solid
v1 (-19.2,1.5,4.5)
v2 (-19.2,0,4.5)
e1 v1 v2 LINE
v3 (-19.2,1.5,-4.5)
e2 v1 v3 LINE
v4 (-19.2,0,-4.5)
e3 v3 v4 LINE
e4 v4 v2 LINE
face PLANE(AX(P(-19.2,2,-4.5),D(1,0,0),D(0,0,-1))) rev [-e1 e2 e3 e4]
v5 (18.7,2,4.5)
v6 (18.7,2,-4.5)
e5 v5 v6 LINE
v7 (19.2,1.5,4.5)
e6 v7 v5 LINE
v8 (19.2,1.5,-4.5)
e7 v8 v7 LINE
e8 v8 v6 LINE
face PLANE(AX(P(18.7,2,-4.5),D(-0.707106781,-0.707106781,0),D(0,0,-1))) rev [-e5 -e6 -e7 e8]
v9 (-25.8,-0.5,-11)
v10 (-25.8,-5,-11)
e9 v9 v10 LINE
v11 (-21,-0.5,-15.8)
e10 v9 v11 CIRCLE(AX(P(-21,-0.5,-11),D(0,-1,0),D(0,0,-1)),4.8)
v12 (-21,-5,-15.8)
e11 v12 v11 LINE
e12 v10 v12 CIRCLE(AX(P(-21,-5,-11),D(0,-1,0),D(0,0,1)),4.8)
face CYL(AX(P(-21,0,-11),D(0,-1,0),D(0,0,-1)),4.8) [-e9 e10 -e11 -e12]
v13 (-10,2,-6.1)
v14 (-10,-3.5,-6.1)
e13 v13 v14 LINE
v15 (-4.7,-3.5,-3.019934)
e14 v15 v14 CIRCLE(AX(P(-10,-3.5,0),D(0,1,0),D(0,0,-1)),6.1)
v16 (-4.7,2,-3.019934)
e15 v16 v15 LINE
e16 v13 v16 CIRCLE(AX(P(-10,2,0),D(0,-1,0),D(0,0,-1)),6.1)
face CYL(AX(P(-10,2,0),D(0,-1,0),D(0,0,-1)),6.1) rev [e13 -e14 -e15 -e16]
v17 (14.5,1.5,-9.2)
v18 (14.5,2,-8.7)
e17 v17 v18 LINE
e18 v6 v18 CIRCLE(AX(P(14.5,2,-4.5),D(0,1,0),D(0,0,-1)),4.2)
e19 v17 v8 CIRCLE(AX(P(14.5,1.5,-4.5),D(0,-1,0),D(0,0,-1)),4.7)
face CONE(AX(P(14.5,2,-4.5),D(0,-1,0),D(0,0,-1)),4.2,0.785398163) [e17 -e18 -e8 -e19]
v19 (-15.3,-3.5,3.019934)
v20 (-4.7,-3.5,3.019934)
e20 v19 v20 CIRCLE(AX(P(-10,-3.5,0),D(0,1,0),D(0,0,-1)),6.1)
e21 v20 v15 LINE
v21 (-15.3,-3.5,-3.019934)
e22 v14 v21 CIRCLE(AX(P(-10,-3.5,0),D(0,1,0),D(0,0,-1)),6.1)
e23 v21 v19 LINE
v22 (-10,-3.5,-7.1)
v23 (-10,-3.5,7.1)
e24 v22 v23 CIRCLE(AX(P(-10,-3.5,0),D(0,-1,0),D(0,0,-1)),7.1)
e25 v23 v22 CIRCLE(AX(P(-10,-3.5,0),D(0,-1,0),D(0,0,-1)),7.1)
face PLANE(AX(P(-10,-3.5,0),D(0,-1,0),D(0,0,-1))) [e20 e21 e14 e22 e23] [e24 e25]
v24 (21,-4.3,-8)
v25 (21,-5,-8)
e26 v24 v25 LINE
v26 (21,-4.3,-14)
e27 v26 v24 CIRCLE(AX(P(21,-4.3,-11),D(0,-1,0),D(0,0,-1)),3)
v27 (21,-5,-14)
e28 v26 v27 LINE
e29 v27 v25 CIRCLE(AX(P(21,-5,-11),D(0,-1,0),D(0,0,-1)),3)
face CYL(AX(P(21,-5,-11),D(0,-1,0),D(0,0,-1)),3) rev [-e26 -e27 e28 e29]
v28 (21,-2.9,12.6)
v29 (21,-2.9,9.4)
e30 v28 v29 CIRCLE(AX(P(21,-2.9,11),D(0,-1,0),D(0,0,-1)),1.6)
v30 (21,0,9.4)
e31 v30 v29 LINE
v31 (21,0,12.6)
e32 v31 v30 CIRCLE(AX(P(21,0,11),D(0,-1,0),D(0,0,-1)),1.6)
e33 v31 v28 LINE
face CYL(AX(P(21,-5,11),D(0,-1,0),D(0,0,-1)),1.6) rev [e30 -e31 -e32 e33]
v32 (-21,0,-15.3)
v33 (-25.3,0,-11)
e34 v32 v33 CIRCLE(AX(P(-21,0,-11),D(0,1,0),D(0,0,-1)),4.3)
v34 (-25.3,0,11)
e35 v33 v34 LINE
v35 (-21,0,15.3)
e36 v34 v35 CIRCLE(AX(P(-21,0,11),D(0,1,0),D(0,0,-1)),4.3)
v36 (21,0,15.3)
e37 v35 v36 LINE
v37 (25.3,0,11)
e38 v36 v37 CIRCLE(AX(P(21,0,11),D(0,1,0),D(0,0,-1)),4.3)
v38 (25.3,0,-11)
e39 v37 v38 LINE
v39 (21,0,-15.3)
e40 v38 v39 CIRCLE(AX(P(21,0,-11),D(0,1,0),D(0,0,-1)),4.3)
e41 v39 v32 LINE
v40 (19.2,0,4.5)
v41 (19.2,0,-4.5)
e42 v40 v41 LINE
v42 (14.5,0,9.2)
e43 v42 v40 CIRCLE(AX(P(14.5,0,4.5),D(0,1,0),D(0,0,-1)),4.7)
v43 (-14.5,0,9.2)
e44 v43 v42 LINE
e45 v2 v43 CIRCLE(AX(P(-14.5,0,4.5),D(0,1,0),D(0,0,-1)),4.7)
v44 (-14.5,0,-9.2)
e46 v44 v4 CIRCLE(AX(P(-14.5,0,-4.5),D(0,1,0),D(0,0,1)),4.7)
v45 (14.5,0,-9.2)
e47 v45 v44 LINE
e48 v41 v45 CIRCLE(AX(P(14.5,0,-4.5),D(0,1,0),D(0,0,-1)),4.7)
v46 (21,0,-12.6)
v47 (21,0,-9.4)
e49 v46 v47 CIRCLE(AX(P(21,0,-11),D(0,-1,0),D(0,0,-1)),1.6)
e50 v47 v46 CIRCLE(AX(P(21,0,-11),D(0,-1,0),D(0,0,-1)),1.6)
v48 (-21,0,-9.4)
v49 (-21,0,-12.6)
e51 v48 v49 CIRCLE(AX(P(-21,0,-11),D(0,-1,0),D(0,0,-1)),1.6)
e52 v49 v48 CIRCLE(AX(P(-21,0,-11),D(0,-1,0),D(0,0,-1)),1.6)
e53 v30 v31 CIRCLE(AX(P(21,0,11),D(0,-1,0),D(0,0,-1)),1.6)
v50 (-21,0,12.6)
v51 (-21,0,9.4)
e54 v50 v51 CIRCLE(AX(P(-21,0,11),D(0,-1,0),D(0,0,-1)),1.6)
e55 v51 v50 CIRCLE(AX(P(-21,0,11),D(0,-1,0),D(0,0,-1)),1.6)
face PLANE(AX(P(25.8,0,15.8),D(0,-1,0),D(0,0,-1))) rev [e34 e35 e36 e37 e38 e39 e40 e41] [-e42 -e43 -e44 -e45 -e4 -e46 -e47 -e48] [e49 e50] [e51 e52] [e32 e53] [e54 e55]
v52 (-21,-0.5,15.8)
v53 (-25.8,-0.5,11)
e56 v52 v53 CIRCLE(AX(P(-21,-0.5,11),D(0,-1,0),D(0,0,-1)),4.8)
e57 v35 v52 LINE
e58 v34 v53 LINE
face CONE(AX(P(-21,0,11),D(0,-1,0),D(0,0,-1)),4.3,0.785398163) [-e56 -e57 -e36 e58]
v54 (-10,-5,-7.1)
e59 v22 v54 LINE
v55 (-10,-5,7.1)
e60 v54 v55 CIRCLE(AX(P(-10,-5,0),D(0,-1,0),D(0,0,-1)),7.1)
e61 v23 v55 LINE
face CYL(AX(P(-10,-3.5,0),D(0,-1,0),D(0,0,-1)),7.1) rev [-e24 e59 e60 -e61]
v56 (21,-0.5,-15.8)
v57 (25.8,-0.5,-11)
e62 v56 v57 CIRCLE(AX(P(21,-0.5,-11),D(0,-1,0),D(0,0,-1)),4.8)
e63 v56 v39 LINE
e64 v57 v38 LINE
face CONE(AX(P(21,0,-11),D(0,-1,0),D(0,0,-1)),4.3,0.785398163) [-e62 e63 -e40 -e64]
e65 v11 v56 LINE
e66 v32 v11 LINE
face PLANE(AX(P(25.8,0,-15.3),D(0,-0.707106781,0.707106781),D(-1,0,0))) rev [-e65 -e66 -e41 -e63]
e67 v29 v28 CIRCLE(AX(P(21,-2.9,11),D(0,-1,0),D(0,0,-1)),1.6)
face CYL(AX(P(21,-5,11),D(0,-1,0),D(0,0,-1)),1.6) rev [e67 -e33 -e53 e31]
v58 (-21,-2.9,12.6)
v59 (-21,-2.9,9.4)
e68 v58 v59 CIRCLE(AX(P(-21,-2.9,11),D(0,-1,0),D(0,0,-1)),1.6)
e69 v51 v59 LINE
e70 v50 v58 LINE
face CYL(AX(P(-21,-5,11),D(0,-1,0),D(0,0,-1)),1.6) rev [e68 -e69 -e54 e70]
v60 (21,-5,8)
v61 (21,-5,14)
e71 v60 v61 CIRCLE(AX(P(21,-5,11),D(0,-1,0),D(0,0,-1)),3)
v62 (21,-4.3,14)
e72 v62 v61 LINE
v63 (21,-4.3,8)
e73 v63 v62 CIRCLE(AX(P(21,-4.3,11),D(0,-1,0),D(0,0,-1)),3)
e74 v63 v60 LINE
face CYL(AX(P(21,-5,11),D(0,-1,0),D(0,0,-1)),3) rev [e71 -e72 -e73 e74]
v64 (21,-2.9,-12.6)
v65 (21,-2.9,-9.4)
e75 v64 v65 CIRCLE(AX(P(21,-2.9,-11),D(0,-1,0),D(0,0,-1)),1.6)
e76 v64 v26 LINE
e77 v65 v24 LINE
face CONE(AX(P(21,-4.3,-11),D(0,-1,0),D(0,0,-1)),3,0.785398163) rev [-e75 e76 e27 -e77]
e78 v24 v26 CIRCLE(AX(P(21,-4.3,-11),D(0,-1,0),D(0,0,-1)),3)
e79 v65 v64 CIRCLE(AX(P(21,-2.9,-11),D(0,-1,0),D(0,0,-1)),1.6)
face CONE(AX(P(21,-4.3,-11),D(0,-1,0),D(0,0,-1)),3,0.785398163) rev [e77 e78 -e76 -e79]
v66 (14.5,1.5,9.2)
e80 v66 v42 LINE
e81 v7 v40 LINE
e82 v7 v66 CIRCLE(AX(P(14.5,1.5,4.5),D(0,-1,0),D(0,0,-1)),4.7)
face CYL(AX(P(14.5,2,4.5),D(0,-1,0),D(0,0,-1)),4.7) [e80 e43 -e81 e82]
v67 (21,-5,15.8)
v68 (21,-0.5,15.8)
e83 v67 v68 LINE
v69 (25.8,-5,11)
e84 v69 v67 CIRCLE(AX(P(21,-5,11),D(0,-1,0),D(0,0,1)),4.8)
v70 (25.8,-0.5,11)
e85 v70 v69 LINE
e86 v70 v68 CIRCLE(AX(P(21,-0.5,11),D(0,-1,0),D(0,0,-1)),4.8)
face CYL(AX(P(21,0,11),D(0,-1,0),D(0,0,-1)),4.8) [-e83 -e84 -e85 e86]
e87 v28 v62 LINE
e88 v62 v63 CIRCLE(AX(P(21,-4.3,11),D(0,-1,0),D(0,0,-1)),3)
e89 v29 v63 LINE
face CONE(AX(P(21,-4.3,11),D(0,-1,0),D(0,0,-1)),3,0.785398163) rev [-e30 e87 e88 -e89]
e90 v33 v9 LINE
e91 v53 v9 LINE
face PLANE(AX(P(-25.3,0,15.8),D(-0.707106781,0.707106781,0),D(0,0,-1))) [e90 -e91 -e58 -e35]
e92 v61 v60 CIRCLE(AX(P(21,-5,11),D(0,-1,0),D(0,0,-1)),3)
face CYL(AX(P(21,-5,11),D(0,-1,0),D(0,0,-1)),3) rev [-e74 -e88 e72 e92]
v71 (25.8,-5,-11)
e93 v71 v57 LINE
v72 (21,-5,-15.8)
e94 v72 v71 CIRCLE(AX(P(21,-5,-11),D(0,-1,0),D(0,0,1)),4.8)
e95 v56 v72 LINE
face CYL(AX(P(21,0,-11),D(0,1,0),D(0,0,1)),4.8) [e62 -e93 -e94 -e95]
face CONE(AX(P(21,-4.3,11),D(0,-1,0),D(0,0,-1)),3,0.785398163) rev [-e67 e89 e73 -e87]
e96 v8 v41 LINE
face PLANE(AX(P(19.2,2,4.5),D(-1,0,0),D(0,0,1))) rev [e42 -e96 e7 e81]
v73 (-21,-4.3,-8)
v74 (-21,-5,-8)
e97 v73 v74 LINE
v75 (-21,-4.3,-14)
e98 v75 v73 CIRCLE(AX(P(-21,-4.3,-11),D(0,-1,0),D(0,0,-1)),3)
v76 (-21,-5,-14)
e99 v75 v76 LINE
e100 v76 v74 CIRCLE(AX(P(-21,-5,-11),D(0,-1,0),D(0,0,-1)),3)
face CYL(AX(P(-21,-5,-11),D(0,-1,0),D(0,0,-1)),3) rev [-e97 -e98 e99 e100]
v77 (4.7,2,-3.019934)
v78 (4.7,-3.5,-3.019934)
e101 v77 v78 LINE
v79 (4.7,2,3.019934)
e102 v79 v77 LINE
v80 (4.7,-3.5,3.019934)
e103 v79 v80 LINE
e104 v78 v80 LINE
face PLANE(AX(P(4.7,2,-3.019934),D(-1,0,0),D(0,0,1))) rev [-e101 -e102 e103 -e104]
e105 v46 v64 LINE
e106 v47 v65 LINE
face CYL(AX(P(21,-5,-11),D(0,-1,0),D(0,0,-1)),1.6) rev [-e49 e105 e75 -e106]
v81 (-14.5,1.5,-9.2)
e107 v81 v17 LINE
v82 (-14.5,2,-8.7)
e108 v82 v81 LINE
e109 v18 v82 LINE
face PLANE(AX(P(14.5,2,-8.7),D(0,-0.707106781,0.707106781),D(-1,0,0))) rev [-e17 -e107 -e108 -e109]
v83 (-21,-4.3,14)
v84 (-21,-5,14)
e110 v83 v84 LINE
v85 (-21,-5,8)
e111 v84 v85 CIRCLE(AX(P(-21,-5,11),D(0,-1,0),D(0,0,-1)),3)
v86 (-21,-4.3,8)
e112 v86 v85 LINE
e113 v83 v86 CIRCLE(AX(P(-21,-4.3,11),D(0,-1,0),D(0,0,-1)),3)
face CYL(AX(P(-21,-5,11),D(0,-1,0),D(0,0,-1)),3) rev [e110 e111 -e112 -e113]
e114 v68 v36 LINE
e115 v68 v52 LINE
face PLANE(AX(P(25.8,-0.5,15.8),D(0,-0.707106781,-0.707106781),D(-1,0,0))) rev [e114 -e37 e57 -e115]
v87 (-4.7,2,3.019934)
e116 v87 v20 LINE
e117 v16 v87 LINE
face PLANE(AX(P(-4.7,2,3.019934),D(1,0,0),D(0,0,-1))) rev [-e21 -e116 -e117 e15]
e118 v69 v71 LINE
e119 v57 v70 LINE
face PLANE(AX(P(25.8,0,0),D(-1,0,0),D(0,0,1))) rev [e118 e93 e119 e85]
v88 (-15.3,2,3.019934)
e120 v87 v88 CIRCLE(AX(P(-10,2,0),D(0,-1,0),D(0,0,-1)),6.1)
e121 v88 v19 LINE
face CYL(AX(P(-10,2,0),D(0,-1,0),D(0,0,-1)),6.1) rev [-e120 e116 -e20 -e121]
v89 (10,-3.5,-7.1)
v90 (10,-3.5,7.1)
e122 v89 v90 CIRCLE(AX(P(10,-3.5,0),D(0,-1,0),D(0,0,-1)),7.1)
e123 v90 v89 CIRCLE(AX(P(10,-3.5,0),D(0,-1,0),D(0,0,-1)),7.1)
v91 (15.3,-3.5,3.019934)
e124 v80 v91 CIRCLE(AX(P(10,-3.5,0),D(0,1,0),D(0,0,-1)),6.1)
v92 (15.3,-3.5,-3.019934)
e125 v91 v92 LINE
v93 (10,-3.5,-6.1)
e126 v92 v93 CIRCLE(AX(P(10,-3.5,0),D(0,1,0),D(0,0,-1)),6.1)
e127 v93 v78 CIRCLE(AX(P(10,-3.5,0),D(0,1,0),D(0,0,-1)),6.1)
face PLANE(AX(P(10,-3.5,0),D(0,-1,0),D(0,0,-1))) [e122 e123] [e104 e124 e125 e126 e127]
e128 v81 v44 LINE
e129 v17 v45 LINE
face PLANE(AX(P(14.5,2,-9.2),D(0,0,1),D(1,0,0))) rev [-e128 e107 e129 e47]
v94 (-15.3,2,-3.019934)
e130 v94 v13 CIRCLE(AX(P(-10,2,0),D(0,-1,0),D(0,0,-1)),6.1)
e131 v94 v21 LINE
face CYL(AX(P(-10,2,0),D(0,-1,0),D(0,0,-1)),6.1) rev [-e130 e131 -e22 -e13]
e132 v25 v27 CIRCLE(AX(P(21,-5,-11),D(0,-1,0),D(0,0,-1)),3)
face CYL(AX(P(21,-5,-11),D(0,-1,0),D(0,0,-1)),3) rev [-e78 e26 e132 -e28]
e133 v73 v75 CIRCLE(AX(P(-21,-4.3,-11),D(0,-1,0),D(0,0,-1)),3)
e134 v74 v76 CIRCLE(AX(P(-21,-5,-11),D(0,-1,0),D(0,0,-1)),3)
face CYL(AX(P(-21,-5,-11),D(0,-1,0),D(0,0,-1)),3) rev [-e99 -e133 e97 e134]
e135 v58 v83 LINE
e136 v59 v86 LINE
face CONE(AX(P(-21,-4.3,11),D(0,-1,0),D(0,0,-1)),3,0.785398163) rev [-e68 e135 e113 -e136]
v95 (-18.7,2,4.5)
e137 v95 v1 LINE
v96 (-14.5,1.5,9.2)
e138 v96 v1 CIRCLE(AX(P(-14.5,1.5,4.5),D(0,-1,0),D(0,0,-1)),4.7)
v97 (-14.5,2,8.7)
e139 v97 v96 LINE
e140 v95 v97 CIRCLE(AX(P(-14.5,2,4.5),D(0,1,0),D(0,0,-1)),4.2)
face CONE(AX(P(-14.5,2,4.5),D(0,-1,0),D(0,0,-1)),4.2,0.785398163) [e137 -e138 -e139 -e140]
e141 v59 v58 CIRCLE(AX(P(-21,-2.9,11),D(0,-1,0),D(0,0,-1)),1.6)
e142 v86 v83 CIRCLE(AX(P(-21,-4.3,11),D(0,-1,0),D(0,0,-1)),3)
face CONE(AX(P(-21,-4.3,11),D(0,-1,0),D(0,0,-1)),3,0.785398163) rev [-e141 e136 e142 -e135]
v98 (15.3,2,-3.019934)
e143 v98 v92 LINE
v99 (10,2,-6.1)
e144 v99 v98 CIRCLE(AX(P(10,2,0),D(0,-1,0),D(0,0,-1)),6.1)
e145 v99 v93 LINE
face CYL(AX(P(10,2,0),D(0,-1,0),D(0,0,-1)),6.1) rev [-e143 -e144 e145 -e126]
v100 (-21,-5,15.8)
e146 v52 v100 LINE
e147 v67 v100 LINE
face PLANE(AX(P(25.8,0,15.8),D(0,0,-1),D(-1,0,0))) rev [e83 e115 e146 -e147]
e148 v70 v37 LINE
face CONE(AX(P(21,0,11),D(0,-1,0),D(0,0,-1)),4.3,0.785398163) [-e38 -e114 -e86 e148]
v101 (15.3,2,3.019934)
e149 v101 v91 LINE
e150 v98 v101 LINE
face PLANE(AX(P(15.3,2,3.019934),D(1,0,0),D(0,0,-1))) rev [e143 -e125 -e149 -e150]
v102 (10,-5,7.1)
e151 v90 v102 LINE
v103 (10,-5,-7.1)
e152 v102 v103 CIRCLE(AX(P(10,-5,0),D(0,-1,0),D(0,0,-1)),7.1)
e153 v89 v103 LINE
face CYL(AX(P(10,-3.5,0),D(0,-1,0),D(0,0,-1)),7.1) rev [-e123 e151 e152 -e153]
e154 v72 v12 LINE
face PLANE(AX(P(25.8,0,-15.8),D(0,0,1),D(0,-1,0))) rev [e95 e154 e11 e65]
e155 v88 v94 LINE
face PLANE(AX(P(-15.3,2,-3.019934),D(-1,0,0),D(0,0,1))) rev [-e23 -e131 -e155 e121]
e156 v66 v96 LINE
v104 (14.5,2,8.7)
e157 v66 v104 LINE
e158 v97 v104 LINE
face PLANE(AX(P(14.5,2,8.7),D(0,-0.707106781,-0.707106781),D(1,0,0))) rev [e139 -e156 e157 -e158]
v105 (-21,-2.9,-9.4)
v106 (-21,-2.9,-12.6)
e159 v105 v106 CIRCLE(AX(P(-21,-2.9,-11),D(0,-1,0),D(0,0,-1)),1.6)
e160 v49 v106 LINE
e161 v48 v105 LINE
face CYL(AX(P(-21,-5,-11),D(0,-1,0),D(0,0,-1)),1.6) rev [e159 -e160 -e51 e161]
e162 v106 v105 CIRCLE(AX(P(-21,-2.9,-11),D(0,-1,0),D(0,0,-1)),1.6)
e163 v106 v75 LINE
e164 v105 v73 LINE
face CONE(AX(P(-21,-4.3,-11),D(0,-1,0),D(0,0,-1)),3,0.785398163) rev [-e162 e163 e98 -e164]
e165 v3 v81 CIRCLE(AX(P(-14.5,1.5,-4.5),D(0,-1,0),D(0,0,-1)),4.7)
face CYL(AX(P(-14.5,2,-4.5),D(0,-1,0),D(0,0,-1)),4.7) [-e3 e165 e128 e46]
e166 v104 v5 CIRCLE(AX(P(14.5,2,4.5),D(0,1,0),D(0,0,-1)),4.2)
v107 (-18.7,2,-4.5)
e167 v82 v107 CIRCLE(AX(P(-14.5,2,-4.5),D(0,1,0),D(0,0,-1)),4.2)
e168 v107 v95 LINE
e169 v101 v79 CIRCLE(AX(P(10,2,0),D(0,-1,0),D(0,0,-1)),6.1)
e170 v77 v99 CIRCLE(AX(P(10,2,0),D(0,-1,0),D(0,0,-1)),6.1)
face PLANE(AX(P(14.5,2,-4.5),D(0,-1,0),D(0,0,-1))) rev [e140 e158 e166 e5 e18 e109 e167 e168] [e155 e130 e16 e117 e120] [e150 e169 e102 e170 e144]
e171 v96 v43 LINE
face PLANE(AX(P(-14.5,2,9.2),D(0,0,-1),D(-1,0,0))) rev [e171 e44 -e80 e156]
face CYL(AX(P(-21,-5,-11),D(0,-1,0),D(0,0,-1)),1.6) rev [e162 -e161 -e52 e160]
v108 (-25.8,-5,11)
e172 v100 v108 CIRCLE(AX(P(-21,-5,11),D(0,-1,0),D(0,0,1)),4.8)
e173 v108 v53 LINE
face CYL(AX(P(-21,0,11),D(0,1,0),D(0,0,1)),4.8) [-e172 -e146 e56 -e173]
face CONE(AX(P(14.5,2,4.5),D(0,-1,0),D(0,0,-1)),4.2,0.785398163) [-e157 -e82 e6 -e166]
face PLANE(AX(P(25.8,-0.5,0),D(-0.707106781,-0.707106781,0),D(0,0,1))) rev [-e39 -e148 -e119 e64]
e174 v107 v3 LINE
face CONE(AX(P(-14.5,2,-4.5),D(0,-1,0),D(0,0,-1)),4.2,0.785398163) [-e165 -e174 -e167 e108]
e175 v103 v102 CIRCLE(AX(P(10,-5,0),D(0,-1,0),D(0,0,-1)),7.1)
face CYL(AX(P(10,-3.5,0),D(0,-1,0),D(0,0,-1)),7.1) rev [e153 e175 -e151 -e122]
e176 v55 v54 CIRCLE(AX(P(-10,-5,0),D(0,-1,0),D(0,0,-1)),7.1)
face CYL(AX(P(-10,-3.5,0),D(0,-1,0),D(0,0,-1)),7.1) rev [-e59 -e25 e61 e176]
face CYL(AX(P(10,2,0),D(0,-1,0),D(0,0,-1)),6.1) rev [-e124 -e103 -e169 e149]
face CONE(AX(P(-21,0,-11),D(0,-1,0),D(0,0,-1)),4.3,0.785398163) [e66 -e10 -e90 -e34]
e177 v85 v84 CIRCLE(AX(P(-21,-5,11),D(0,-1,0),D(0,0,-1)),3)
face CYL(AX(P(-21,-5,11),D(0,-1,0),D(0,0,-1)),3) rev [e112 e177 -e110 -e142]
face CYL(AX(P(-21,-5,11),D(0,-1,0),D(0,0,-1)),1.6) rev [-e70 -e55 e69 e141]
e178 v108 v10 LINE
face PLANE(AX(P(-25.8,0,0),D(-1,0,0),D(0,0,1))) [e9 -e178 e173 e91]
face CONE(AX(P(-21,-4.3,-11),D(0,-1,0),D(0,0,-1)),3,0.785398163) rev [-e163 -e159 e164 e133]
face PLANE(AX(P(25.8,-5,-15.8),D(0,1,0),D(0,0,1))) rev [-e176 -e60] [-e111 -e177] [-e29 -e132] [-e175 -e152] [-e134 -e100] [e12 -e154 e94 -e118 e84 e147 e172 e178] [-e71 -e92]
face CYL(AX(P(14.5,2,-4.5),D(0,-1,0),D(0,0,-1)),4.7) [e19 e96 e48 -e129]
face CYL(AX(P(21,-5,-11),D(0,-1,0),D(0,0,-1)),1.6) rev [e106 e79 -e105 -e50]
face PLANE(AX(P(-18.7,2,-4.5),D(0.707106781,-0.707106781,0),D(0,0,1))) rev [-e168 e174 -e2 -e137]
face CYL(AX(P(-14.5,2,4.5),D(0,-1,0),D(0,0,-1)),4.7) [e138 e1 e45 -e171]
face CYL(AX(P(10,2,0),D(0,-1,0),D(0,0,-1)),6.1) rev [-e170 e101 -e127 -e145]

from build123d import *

# Parameters (mm, degrees)
SKETCH_1_W               = 31.6
SKETCH_1_H               = 5
EXTRUDE_1_DEPTH          = 25.8
EXTRUDE_2_DEPTH          = 2
FILLET_1_R               = 4.8
CUT_EXTRUDE_1_DEPTH      = 32.052858162
SKETCH_4_R               = 7.1
CUT_EXTRUDE_2_DEPTH      = 1.5
CHAMFER_2_SIZE           = 0.5
HOLE_WIZARD_1_AT_2_COUNT = 2
HOLE_WIZARD_1_AT_2_PITCH = 42
HOLE_WIZARD_1_AT_3_COUNT = 2
HOLE_WIZARD_1_AT_3_PITCH = 47.413078365
HOLE_WIZARD_1_AT_4_COUNT = 2
HOLE_WIZARD_1_AT_4_PITCH = 22


with BuildPart() as part:
    # 草图1 → 凸台-拉伸1 (new, symmetric)
    with BuildSketch(Plane(origin=(0, 0, 0), x_dir=(0, 0, -1), z_dir=(1, 0, 0))):
        with Locations((0, -2.5)):
            Rectangle(SKETCH_1_W, SKETCH_1_H)
    extrude(amount=EXTRUDE_1_DEPTH, both=True)

    # 草图2 → 凸台-拉伸2 (add)
    with BuildSketch(Plane(origin=(0, 0, 0), x_dir=(1, 0, 0), z_dir=(0, 1, 0))):
        with BuildLine():
            Line((-19.2, 4.5), (-19.2, -4.5))
            ThreePointArc((-19.2, -4.5), (-17.823401872, -7.823401872), (-14.5, -9.2))
            Line((-14.5, -9.2), (14.5, -9.2))
            ThreePointArc((14.5, -9.2), (17.823401872, -7.823401872), (19.2, -4.5))
            Line((19.2, -4.5), (19.2, 4.5))
            ThreePointArc((19.2, 4.5), (17.823401872, 7.823401872), (14.5, 9.2))
            Line((14.5, 9.2), (-14.5, 9.2))
            ThreePointArc((-14.5, 9.2), (-17.823401872, 7.823401872), (-19.2, 4.5))
        make_face()
    extrude(amount=EXTRUDE_2_DEPTH)

    # 圆角1
    fillet_1_edges = [part.edges().sort_by_distance(p)[0] for p in [
        (25.8, -2.5, 15.8),
        (25.8, -2.5, -15.8),
        (-25.8, -2.5, 15.8),
        (-25.8, -2.5, -15.8),
    ]]
    fillet(fillet_1_edges, radius=FILLET_1_R)

    # 草图3 → 切除-拉伸1 (cut, through all)
    with BuildSketch(Plane.XZ.offset(5)):
        with BuildLine():
            Line((-15.3, -3.019933774), (-15.3, 3.019933774))
            ThreePointArc((-15.3, 3.019933774), (-10, 6.1), (-4.7, 3.019933774))
            Line((-4.7, 3.019933774), (-4.7, -3.019933774))
            ThreePointArc((-4.7, -3.019933774), (-10, -6.1), (-15.3, -3.019933774))
        make_face()
        with BuildLine():
            Line((15.3, 3.019933774), (15.3, -3.019933774))
            ThreePointArc((15.3, -3.019933774), (10, -6.1), (4.7, -3.019933774))
            Line((4.7, -3.019933774), (4.7, 3.019933774))
            ThreePointArc((4.7, 3.019933774), (10, 6.1), (15.3, 3.019933774))
        make_face()
    extrude(amount=-CUT_EXTRUDE_1_DEPTH, mode=Mode.SUBTRACT)

    # 草图4 → 切除-拉伸2 (cut)
    with BuildSketch(Plane.XZ.offset(5)):
        with Locations(Location((-10, 0, 0), (0, 0, 270))):
            Circle(SKETCH_4_R)
        with Locations(Location((10, 0, 0), (0, 0, 270))):
            Circle(SKETCH_4_R)
    extrude(amount=-CUT_EXTRUDE_2_DEPTH, mode=Mode.SUBTRACT)

    # 倒角2
    chamfer_2_edges = [part.edges().sort_by_distance(p)[0] for p in [
        (17.823401872, 2, -7.823401872),
        (0, 2, -9.2),
        (-17.823401872, 2, -7.823401872),
        (-19.2, 2, 0),
        (-17.823401872, 2, 7.823401872),
        (0, 2, 9.2),
        (17.823401872, 2, 7.823401872),
        (19.2, 2, 0),
        (25.8, 0, 0),
        (-25.8, 0, 0),
        (0, 0, 15.8),
        (0, 0, -15.8),
        (-24.39411255, 0, 14.39411255),
        (-24.39411255, 0, -14.39411255),
        (24.39411255, 0, 14.39411255),
        (24.39411255, 0, -14.39411255),
    ]]
    chamfer(chamfer_2_edges, length=CHAMFER_2_SIZE)

    # 草图6 → 打孔尺寸(%根据十字)槽半沉头木螺钉的类型1 (revolve, cut)
    with BuildSketch(Plane(origin=(-21, -5, 11), x_dir=(0, 0, -1), z_dir=(1, 0, 0))):
        Polygon((0, 0), (0, 6.16137699), (1.6, 5.2), (1.6, 2.1), (3, 0.7), (3, 0), align=None)
    hole_wizard_1 = revolve(axis=Axis((-21, -11.35, 11), (0, 1, 0)), mode=Mode.SUBTRACT)

    # 打孔尺寸(%根据十字)槽半沉头木螺钉的类型1 at 2: 打孔尺寸(%根据十字)槽半沉头木螺钉的类型1 ×2
    with Locations(*[(i * HOLE_WIZARD_1_AT_2_PITCH, 0, 0) for i in range(1, HOLE_WIZARD_1_AT_2_COUNT)]):
        add(hole_wizard_1, mode=Mode.SUBTRACT)

    # 打孔尺寸(%根据十字)槽半沉头木螺钉的类型1 at 3: 打孔尺寸(%根据十字)槽半沉头木螺钉的类型1 ×2
    with Locations(*[Vector(0.8858315352801553, 0, -0.4640069946705578) * (i * HOLE_WIZARD_1_AT_3_PITCH) for i in range(1, HOLE_WIZARD_1_AT_3_COUNT)]):
        add(hole_wizard_1, mode=Mode.SUBTRACT)

    # 打孔尺寸(%根据十字)槽半沉头木螺钉的类型1 at 4: 打孔尺寸(%根据十字)槽半沉头木螺钉的类型1 ×2
    with Locations(*[(0, 0, -i * HOLE_WIZARD_1_AT_4_PITCH) for i in range(1, HOLE_WIZARD_1_AT_4_COUNT)]):
        add(hole_wizard_1, mode=Mode.SUBTRACT)


solid = part.part
